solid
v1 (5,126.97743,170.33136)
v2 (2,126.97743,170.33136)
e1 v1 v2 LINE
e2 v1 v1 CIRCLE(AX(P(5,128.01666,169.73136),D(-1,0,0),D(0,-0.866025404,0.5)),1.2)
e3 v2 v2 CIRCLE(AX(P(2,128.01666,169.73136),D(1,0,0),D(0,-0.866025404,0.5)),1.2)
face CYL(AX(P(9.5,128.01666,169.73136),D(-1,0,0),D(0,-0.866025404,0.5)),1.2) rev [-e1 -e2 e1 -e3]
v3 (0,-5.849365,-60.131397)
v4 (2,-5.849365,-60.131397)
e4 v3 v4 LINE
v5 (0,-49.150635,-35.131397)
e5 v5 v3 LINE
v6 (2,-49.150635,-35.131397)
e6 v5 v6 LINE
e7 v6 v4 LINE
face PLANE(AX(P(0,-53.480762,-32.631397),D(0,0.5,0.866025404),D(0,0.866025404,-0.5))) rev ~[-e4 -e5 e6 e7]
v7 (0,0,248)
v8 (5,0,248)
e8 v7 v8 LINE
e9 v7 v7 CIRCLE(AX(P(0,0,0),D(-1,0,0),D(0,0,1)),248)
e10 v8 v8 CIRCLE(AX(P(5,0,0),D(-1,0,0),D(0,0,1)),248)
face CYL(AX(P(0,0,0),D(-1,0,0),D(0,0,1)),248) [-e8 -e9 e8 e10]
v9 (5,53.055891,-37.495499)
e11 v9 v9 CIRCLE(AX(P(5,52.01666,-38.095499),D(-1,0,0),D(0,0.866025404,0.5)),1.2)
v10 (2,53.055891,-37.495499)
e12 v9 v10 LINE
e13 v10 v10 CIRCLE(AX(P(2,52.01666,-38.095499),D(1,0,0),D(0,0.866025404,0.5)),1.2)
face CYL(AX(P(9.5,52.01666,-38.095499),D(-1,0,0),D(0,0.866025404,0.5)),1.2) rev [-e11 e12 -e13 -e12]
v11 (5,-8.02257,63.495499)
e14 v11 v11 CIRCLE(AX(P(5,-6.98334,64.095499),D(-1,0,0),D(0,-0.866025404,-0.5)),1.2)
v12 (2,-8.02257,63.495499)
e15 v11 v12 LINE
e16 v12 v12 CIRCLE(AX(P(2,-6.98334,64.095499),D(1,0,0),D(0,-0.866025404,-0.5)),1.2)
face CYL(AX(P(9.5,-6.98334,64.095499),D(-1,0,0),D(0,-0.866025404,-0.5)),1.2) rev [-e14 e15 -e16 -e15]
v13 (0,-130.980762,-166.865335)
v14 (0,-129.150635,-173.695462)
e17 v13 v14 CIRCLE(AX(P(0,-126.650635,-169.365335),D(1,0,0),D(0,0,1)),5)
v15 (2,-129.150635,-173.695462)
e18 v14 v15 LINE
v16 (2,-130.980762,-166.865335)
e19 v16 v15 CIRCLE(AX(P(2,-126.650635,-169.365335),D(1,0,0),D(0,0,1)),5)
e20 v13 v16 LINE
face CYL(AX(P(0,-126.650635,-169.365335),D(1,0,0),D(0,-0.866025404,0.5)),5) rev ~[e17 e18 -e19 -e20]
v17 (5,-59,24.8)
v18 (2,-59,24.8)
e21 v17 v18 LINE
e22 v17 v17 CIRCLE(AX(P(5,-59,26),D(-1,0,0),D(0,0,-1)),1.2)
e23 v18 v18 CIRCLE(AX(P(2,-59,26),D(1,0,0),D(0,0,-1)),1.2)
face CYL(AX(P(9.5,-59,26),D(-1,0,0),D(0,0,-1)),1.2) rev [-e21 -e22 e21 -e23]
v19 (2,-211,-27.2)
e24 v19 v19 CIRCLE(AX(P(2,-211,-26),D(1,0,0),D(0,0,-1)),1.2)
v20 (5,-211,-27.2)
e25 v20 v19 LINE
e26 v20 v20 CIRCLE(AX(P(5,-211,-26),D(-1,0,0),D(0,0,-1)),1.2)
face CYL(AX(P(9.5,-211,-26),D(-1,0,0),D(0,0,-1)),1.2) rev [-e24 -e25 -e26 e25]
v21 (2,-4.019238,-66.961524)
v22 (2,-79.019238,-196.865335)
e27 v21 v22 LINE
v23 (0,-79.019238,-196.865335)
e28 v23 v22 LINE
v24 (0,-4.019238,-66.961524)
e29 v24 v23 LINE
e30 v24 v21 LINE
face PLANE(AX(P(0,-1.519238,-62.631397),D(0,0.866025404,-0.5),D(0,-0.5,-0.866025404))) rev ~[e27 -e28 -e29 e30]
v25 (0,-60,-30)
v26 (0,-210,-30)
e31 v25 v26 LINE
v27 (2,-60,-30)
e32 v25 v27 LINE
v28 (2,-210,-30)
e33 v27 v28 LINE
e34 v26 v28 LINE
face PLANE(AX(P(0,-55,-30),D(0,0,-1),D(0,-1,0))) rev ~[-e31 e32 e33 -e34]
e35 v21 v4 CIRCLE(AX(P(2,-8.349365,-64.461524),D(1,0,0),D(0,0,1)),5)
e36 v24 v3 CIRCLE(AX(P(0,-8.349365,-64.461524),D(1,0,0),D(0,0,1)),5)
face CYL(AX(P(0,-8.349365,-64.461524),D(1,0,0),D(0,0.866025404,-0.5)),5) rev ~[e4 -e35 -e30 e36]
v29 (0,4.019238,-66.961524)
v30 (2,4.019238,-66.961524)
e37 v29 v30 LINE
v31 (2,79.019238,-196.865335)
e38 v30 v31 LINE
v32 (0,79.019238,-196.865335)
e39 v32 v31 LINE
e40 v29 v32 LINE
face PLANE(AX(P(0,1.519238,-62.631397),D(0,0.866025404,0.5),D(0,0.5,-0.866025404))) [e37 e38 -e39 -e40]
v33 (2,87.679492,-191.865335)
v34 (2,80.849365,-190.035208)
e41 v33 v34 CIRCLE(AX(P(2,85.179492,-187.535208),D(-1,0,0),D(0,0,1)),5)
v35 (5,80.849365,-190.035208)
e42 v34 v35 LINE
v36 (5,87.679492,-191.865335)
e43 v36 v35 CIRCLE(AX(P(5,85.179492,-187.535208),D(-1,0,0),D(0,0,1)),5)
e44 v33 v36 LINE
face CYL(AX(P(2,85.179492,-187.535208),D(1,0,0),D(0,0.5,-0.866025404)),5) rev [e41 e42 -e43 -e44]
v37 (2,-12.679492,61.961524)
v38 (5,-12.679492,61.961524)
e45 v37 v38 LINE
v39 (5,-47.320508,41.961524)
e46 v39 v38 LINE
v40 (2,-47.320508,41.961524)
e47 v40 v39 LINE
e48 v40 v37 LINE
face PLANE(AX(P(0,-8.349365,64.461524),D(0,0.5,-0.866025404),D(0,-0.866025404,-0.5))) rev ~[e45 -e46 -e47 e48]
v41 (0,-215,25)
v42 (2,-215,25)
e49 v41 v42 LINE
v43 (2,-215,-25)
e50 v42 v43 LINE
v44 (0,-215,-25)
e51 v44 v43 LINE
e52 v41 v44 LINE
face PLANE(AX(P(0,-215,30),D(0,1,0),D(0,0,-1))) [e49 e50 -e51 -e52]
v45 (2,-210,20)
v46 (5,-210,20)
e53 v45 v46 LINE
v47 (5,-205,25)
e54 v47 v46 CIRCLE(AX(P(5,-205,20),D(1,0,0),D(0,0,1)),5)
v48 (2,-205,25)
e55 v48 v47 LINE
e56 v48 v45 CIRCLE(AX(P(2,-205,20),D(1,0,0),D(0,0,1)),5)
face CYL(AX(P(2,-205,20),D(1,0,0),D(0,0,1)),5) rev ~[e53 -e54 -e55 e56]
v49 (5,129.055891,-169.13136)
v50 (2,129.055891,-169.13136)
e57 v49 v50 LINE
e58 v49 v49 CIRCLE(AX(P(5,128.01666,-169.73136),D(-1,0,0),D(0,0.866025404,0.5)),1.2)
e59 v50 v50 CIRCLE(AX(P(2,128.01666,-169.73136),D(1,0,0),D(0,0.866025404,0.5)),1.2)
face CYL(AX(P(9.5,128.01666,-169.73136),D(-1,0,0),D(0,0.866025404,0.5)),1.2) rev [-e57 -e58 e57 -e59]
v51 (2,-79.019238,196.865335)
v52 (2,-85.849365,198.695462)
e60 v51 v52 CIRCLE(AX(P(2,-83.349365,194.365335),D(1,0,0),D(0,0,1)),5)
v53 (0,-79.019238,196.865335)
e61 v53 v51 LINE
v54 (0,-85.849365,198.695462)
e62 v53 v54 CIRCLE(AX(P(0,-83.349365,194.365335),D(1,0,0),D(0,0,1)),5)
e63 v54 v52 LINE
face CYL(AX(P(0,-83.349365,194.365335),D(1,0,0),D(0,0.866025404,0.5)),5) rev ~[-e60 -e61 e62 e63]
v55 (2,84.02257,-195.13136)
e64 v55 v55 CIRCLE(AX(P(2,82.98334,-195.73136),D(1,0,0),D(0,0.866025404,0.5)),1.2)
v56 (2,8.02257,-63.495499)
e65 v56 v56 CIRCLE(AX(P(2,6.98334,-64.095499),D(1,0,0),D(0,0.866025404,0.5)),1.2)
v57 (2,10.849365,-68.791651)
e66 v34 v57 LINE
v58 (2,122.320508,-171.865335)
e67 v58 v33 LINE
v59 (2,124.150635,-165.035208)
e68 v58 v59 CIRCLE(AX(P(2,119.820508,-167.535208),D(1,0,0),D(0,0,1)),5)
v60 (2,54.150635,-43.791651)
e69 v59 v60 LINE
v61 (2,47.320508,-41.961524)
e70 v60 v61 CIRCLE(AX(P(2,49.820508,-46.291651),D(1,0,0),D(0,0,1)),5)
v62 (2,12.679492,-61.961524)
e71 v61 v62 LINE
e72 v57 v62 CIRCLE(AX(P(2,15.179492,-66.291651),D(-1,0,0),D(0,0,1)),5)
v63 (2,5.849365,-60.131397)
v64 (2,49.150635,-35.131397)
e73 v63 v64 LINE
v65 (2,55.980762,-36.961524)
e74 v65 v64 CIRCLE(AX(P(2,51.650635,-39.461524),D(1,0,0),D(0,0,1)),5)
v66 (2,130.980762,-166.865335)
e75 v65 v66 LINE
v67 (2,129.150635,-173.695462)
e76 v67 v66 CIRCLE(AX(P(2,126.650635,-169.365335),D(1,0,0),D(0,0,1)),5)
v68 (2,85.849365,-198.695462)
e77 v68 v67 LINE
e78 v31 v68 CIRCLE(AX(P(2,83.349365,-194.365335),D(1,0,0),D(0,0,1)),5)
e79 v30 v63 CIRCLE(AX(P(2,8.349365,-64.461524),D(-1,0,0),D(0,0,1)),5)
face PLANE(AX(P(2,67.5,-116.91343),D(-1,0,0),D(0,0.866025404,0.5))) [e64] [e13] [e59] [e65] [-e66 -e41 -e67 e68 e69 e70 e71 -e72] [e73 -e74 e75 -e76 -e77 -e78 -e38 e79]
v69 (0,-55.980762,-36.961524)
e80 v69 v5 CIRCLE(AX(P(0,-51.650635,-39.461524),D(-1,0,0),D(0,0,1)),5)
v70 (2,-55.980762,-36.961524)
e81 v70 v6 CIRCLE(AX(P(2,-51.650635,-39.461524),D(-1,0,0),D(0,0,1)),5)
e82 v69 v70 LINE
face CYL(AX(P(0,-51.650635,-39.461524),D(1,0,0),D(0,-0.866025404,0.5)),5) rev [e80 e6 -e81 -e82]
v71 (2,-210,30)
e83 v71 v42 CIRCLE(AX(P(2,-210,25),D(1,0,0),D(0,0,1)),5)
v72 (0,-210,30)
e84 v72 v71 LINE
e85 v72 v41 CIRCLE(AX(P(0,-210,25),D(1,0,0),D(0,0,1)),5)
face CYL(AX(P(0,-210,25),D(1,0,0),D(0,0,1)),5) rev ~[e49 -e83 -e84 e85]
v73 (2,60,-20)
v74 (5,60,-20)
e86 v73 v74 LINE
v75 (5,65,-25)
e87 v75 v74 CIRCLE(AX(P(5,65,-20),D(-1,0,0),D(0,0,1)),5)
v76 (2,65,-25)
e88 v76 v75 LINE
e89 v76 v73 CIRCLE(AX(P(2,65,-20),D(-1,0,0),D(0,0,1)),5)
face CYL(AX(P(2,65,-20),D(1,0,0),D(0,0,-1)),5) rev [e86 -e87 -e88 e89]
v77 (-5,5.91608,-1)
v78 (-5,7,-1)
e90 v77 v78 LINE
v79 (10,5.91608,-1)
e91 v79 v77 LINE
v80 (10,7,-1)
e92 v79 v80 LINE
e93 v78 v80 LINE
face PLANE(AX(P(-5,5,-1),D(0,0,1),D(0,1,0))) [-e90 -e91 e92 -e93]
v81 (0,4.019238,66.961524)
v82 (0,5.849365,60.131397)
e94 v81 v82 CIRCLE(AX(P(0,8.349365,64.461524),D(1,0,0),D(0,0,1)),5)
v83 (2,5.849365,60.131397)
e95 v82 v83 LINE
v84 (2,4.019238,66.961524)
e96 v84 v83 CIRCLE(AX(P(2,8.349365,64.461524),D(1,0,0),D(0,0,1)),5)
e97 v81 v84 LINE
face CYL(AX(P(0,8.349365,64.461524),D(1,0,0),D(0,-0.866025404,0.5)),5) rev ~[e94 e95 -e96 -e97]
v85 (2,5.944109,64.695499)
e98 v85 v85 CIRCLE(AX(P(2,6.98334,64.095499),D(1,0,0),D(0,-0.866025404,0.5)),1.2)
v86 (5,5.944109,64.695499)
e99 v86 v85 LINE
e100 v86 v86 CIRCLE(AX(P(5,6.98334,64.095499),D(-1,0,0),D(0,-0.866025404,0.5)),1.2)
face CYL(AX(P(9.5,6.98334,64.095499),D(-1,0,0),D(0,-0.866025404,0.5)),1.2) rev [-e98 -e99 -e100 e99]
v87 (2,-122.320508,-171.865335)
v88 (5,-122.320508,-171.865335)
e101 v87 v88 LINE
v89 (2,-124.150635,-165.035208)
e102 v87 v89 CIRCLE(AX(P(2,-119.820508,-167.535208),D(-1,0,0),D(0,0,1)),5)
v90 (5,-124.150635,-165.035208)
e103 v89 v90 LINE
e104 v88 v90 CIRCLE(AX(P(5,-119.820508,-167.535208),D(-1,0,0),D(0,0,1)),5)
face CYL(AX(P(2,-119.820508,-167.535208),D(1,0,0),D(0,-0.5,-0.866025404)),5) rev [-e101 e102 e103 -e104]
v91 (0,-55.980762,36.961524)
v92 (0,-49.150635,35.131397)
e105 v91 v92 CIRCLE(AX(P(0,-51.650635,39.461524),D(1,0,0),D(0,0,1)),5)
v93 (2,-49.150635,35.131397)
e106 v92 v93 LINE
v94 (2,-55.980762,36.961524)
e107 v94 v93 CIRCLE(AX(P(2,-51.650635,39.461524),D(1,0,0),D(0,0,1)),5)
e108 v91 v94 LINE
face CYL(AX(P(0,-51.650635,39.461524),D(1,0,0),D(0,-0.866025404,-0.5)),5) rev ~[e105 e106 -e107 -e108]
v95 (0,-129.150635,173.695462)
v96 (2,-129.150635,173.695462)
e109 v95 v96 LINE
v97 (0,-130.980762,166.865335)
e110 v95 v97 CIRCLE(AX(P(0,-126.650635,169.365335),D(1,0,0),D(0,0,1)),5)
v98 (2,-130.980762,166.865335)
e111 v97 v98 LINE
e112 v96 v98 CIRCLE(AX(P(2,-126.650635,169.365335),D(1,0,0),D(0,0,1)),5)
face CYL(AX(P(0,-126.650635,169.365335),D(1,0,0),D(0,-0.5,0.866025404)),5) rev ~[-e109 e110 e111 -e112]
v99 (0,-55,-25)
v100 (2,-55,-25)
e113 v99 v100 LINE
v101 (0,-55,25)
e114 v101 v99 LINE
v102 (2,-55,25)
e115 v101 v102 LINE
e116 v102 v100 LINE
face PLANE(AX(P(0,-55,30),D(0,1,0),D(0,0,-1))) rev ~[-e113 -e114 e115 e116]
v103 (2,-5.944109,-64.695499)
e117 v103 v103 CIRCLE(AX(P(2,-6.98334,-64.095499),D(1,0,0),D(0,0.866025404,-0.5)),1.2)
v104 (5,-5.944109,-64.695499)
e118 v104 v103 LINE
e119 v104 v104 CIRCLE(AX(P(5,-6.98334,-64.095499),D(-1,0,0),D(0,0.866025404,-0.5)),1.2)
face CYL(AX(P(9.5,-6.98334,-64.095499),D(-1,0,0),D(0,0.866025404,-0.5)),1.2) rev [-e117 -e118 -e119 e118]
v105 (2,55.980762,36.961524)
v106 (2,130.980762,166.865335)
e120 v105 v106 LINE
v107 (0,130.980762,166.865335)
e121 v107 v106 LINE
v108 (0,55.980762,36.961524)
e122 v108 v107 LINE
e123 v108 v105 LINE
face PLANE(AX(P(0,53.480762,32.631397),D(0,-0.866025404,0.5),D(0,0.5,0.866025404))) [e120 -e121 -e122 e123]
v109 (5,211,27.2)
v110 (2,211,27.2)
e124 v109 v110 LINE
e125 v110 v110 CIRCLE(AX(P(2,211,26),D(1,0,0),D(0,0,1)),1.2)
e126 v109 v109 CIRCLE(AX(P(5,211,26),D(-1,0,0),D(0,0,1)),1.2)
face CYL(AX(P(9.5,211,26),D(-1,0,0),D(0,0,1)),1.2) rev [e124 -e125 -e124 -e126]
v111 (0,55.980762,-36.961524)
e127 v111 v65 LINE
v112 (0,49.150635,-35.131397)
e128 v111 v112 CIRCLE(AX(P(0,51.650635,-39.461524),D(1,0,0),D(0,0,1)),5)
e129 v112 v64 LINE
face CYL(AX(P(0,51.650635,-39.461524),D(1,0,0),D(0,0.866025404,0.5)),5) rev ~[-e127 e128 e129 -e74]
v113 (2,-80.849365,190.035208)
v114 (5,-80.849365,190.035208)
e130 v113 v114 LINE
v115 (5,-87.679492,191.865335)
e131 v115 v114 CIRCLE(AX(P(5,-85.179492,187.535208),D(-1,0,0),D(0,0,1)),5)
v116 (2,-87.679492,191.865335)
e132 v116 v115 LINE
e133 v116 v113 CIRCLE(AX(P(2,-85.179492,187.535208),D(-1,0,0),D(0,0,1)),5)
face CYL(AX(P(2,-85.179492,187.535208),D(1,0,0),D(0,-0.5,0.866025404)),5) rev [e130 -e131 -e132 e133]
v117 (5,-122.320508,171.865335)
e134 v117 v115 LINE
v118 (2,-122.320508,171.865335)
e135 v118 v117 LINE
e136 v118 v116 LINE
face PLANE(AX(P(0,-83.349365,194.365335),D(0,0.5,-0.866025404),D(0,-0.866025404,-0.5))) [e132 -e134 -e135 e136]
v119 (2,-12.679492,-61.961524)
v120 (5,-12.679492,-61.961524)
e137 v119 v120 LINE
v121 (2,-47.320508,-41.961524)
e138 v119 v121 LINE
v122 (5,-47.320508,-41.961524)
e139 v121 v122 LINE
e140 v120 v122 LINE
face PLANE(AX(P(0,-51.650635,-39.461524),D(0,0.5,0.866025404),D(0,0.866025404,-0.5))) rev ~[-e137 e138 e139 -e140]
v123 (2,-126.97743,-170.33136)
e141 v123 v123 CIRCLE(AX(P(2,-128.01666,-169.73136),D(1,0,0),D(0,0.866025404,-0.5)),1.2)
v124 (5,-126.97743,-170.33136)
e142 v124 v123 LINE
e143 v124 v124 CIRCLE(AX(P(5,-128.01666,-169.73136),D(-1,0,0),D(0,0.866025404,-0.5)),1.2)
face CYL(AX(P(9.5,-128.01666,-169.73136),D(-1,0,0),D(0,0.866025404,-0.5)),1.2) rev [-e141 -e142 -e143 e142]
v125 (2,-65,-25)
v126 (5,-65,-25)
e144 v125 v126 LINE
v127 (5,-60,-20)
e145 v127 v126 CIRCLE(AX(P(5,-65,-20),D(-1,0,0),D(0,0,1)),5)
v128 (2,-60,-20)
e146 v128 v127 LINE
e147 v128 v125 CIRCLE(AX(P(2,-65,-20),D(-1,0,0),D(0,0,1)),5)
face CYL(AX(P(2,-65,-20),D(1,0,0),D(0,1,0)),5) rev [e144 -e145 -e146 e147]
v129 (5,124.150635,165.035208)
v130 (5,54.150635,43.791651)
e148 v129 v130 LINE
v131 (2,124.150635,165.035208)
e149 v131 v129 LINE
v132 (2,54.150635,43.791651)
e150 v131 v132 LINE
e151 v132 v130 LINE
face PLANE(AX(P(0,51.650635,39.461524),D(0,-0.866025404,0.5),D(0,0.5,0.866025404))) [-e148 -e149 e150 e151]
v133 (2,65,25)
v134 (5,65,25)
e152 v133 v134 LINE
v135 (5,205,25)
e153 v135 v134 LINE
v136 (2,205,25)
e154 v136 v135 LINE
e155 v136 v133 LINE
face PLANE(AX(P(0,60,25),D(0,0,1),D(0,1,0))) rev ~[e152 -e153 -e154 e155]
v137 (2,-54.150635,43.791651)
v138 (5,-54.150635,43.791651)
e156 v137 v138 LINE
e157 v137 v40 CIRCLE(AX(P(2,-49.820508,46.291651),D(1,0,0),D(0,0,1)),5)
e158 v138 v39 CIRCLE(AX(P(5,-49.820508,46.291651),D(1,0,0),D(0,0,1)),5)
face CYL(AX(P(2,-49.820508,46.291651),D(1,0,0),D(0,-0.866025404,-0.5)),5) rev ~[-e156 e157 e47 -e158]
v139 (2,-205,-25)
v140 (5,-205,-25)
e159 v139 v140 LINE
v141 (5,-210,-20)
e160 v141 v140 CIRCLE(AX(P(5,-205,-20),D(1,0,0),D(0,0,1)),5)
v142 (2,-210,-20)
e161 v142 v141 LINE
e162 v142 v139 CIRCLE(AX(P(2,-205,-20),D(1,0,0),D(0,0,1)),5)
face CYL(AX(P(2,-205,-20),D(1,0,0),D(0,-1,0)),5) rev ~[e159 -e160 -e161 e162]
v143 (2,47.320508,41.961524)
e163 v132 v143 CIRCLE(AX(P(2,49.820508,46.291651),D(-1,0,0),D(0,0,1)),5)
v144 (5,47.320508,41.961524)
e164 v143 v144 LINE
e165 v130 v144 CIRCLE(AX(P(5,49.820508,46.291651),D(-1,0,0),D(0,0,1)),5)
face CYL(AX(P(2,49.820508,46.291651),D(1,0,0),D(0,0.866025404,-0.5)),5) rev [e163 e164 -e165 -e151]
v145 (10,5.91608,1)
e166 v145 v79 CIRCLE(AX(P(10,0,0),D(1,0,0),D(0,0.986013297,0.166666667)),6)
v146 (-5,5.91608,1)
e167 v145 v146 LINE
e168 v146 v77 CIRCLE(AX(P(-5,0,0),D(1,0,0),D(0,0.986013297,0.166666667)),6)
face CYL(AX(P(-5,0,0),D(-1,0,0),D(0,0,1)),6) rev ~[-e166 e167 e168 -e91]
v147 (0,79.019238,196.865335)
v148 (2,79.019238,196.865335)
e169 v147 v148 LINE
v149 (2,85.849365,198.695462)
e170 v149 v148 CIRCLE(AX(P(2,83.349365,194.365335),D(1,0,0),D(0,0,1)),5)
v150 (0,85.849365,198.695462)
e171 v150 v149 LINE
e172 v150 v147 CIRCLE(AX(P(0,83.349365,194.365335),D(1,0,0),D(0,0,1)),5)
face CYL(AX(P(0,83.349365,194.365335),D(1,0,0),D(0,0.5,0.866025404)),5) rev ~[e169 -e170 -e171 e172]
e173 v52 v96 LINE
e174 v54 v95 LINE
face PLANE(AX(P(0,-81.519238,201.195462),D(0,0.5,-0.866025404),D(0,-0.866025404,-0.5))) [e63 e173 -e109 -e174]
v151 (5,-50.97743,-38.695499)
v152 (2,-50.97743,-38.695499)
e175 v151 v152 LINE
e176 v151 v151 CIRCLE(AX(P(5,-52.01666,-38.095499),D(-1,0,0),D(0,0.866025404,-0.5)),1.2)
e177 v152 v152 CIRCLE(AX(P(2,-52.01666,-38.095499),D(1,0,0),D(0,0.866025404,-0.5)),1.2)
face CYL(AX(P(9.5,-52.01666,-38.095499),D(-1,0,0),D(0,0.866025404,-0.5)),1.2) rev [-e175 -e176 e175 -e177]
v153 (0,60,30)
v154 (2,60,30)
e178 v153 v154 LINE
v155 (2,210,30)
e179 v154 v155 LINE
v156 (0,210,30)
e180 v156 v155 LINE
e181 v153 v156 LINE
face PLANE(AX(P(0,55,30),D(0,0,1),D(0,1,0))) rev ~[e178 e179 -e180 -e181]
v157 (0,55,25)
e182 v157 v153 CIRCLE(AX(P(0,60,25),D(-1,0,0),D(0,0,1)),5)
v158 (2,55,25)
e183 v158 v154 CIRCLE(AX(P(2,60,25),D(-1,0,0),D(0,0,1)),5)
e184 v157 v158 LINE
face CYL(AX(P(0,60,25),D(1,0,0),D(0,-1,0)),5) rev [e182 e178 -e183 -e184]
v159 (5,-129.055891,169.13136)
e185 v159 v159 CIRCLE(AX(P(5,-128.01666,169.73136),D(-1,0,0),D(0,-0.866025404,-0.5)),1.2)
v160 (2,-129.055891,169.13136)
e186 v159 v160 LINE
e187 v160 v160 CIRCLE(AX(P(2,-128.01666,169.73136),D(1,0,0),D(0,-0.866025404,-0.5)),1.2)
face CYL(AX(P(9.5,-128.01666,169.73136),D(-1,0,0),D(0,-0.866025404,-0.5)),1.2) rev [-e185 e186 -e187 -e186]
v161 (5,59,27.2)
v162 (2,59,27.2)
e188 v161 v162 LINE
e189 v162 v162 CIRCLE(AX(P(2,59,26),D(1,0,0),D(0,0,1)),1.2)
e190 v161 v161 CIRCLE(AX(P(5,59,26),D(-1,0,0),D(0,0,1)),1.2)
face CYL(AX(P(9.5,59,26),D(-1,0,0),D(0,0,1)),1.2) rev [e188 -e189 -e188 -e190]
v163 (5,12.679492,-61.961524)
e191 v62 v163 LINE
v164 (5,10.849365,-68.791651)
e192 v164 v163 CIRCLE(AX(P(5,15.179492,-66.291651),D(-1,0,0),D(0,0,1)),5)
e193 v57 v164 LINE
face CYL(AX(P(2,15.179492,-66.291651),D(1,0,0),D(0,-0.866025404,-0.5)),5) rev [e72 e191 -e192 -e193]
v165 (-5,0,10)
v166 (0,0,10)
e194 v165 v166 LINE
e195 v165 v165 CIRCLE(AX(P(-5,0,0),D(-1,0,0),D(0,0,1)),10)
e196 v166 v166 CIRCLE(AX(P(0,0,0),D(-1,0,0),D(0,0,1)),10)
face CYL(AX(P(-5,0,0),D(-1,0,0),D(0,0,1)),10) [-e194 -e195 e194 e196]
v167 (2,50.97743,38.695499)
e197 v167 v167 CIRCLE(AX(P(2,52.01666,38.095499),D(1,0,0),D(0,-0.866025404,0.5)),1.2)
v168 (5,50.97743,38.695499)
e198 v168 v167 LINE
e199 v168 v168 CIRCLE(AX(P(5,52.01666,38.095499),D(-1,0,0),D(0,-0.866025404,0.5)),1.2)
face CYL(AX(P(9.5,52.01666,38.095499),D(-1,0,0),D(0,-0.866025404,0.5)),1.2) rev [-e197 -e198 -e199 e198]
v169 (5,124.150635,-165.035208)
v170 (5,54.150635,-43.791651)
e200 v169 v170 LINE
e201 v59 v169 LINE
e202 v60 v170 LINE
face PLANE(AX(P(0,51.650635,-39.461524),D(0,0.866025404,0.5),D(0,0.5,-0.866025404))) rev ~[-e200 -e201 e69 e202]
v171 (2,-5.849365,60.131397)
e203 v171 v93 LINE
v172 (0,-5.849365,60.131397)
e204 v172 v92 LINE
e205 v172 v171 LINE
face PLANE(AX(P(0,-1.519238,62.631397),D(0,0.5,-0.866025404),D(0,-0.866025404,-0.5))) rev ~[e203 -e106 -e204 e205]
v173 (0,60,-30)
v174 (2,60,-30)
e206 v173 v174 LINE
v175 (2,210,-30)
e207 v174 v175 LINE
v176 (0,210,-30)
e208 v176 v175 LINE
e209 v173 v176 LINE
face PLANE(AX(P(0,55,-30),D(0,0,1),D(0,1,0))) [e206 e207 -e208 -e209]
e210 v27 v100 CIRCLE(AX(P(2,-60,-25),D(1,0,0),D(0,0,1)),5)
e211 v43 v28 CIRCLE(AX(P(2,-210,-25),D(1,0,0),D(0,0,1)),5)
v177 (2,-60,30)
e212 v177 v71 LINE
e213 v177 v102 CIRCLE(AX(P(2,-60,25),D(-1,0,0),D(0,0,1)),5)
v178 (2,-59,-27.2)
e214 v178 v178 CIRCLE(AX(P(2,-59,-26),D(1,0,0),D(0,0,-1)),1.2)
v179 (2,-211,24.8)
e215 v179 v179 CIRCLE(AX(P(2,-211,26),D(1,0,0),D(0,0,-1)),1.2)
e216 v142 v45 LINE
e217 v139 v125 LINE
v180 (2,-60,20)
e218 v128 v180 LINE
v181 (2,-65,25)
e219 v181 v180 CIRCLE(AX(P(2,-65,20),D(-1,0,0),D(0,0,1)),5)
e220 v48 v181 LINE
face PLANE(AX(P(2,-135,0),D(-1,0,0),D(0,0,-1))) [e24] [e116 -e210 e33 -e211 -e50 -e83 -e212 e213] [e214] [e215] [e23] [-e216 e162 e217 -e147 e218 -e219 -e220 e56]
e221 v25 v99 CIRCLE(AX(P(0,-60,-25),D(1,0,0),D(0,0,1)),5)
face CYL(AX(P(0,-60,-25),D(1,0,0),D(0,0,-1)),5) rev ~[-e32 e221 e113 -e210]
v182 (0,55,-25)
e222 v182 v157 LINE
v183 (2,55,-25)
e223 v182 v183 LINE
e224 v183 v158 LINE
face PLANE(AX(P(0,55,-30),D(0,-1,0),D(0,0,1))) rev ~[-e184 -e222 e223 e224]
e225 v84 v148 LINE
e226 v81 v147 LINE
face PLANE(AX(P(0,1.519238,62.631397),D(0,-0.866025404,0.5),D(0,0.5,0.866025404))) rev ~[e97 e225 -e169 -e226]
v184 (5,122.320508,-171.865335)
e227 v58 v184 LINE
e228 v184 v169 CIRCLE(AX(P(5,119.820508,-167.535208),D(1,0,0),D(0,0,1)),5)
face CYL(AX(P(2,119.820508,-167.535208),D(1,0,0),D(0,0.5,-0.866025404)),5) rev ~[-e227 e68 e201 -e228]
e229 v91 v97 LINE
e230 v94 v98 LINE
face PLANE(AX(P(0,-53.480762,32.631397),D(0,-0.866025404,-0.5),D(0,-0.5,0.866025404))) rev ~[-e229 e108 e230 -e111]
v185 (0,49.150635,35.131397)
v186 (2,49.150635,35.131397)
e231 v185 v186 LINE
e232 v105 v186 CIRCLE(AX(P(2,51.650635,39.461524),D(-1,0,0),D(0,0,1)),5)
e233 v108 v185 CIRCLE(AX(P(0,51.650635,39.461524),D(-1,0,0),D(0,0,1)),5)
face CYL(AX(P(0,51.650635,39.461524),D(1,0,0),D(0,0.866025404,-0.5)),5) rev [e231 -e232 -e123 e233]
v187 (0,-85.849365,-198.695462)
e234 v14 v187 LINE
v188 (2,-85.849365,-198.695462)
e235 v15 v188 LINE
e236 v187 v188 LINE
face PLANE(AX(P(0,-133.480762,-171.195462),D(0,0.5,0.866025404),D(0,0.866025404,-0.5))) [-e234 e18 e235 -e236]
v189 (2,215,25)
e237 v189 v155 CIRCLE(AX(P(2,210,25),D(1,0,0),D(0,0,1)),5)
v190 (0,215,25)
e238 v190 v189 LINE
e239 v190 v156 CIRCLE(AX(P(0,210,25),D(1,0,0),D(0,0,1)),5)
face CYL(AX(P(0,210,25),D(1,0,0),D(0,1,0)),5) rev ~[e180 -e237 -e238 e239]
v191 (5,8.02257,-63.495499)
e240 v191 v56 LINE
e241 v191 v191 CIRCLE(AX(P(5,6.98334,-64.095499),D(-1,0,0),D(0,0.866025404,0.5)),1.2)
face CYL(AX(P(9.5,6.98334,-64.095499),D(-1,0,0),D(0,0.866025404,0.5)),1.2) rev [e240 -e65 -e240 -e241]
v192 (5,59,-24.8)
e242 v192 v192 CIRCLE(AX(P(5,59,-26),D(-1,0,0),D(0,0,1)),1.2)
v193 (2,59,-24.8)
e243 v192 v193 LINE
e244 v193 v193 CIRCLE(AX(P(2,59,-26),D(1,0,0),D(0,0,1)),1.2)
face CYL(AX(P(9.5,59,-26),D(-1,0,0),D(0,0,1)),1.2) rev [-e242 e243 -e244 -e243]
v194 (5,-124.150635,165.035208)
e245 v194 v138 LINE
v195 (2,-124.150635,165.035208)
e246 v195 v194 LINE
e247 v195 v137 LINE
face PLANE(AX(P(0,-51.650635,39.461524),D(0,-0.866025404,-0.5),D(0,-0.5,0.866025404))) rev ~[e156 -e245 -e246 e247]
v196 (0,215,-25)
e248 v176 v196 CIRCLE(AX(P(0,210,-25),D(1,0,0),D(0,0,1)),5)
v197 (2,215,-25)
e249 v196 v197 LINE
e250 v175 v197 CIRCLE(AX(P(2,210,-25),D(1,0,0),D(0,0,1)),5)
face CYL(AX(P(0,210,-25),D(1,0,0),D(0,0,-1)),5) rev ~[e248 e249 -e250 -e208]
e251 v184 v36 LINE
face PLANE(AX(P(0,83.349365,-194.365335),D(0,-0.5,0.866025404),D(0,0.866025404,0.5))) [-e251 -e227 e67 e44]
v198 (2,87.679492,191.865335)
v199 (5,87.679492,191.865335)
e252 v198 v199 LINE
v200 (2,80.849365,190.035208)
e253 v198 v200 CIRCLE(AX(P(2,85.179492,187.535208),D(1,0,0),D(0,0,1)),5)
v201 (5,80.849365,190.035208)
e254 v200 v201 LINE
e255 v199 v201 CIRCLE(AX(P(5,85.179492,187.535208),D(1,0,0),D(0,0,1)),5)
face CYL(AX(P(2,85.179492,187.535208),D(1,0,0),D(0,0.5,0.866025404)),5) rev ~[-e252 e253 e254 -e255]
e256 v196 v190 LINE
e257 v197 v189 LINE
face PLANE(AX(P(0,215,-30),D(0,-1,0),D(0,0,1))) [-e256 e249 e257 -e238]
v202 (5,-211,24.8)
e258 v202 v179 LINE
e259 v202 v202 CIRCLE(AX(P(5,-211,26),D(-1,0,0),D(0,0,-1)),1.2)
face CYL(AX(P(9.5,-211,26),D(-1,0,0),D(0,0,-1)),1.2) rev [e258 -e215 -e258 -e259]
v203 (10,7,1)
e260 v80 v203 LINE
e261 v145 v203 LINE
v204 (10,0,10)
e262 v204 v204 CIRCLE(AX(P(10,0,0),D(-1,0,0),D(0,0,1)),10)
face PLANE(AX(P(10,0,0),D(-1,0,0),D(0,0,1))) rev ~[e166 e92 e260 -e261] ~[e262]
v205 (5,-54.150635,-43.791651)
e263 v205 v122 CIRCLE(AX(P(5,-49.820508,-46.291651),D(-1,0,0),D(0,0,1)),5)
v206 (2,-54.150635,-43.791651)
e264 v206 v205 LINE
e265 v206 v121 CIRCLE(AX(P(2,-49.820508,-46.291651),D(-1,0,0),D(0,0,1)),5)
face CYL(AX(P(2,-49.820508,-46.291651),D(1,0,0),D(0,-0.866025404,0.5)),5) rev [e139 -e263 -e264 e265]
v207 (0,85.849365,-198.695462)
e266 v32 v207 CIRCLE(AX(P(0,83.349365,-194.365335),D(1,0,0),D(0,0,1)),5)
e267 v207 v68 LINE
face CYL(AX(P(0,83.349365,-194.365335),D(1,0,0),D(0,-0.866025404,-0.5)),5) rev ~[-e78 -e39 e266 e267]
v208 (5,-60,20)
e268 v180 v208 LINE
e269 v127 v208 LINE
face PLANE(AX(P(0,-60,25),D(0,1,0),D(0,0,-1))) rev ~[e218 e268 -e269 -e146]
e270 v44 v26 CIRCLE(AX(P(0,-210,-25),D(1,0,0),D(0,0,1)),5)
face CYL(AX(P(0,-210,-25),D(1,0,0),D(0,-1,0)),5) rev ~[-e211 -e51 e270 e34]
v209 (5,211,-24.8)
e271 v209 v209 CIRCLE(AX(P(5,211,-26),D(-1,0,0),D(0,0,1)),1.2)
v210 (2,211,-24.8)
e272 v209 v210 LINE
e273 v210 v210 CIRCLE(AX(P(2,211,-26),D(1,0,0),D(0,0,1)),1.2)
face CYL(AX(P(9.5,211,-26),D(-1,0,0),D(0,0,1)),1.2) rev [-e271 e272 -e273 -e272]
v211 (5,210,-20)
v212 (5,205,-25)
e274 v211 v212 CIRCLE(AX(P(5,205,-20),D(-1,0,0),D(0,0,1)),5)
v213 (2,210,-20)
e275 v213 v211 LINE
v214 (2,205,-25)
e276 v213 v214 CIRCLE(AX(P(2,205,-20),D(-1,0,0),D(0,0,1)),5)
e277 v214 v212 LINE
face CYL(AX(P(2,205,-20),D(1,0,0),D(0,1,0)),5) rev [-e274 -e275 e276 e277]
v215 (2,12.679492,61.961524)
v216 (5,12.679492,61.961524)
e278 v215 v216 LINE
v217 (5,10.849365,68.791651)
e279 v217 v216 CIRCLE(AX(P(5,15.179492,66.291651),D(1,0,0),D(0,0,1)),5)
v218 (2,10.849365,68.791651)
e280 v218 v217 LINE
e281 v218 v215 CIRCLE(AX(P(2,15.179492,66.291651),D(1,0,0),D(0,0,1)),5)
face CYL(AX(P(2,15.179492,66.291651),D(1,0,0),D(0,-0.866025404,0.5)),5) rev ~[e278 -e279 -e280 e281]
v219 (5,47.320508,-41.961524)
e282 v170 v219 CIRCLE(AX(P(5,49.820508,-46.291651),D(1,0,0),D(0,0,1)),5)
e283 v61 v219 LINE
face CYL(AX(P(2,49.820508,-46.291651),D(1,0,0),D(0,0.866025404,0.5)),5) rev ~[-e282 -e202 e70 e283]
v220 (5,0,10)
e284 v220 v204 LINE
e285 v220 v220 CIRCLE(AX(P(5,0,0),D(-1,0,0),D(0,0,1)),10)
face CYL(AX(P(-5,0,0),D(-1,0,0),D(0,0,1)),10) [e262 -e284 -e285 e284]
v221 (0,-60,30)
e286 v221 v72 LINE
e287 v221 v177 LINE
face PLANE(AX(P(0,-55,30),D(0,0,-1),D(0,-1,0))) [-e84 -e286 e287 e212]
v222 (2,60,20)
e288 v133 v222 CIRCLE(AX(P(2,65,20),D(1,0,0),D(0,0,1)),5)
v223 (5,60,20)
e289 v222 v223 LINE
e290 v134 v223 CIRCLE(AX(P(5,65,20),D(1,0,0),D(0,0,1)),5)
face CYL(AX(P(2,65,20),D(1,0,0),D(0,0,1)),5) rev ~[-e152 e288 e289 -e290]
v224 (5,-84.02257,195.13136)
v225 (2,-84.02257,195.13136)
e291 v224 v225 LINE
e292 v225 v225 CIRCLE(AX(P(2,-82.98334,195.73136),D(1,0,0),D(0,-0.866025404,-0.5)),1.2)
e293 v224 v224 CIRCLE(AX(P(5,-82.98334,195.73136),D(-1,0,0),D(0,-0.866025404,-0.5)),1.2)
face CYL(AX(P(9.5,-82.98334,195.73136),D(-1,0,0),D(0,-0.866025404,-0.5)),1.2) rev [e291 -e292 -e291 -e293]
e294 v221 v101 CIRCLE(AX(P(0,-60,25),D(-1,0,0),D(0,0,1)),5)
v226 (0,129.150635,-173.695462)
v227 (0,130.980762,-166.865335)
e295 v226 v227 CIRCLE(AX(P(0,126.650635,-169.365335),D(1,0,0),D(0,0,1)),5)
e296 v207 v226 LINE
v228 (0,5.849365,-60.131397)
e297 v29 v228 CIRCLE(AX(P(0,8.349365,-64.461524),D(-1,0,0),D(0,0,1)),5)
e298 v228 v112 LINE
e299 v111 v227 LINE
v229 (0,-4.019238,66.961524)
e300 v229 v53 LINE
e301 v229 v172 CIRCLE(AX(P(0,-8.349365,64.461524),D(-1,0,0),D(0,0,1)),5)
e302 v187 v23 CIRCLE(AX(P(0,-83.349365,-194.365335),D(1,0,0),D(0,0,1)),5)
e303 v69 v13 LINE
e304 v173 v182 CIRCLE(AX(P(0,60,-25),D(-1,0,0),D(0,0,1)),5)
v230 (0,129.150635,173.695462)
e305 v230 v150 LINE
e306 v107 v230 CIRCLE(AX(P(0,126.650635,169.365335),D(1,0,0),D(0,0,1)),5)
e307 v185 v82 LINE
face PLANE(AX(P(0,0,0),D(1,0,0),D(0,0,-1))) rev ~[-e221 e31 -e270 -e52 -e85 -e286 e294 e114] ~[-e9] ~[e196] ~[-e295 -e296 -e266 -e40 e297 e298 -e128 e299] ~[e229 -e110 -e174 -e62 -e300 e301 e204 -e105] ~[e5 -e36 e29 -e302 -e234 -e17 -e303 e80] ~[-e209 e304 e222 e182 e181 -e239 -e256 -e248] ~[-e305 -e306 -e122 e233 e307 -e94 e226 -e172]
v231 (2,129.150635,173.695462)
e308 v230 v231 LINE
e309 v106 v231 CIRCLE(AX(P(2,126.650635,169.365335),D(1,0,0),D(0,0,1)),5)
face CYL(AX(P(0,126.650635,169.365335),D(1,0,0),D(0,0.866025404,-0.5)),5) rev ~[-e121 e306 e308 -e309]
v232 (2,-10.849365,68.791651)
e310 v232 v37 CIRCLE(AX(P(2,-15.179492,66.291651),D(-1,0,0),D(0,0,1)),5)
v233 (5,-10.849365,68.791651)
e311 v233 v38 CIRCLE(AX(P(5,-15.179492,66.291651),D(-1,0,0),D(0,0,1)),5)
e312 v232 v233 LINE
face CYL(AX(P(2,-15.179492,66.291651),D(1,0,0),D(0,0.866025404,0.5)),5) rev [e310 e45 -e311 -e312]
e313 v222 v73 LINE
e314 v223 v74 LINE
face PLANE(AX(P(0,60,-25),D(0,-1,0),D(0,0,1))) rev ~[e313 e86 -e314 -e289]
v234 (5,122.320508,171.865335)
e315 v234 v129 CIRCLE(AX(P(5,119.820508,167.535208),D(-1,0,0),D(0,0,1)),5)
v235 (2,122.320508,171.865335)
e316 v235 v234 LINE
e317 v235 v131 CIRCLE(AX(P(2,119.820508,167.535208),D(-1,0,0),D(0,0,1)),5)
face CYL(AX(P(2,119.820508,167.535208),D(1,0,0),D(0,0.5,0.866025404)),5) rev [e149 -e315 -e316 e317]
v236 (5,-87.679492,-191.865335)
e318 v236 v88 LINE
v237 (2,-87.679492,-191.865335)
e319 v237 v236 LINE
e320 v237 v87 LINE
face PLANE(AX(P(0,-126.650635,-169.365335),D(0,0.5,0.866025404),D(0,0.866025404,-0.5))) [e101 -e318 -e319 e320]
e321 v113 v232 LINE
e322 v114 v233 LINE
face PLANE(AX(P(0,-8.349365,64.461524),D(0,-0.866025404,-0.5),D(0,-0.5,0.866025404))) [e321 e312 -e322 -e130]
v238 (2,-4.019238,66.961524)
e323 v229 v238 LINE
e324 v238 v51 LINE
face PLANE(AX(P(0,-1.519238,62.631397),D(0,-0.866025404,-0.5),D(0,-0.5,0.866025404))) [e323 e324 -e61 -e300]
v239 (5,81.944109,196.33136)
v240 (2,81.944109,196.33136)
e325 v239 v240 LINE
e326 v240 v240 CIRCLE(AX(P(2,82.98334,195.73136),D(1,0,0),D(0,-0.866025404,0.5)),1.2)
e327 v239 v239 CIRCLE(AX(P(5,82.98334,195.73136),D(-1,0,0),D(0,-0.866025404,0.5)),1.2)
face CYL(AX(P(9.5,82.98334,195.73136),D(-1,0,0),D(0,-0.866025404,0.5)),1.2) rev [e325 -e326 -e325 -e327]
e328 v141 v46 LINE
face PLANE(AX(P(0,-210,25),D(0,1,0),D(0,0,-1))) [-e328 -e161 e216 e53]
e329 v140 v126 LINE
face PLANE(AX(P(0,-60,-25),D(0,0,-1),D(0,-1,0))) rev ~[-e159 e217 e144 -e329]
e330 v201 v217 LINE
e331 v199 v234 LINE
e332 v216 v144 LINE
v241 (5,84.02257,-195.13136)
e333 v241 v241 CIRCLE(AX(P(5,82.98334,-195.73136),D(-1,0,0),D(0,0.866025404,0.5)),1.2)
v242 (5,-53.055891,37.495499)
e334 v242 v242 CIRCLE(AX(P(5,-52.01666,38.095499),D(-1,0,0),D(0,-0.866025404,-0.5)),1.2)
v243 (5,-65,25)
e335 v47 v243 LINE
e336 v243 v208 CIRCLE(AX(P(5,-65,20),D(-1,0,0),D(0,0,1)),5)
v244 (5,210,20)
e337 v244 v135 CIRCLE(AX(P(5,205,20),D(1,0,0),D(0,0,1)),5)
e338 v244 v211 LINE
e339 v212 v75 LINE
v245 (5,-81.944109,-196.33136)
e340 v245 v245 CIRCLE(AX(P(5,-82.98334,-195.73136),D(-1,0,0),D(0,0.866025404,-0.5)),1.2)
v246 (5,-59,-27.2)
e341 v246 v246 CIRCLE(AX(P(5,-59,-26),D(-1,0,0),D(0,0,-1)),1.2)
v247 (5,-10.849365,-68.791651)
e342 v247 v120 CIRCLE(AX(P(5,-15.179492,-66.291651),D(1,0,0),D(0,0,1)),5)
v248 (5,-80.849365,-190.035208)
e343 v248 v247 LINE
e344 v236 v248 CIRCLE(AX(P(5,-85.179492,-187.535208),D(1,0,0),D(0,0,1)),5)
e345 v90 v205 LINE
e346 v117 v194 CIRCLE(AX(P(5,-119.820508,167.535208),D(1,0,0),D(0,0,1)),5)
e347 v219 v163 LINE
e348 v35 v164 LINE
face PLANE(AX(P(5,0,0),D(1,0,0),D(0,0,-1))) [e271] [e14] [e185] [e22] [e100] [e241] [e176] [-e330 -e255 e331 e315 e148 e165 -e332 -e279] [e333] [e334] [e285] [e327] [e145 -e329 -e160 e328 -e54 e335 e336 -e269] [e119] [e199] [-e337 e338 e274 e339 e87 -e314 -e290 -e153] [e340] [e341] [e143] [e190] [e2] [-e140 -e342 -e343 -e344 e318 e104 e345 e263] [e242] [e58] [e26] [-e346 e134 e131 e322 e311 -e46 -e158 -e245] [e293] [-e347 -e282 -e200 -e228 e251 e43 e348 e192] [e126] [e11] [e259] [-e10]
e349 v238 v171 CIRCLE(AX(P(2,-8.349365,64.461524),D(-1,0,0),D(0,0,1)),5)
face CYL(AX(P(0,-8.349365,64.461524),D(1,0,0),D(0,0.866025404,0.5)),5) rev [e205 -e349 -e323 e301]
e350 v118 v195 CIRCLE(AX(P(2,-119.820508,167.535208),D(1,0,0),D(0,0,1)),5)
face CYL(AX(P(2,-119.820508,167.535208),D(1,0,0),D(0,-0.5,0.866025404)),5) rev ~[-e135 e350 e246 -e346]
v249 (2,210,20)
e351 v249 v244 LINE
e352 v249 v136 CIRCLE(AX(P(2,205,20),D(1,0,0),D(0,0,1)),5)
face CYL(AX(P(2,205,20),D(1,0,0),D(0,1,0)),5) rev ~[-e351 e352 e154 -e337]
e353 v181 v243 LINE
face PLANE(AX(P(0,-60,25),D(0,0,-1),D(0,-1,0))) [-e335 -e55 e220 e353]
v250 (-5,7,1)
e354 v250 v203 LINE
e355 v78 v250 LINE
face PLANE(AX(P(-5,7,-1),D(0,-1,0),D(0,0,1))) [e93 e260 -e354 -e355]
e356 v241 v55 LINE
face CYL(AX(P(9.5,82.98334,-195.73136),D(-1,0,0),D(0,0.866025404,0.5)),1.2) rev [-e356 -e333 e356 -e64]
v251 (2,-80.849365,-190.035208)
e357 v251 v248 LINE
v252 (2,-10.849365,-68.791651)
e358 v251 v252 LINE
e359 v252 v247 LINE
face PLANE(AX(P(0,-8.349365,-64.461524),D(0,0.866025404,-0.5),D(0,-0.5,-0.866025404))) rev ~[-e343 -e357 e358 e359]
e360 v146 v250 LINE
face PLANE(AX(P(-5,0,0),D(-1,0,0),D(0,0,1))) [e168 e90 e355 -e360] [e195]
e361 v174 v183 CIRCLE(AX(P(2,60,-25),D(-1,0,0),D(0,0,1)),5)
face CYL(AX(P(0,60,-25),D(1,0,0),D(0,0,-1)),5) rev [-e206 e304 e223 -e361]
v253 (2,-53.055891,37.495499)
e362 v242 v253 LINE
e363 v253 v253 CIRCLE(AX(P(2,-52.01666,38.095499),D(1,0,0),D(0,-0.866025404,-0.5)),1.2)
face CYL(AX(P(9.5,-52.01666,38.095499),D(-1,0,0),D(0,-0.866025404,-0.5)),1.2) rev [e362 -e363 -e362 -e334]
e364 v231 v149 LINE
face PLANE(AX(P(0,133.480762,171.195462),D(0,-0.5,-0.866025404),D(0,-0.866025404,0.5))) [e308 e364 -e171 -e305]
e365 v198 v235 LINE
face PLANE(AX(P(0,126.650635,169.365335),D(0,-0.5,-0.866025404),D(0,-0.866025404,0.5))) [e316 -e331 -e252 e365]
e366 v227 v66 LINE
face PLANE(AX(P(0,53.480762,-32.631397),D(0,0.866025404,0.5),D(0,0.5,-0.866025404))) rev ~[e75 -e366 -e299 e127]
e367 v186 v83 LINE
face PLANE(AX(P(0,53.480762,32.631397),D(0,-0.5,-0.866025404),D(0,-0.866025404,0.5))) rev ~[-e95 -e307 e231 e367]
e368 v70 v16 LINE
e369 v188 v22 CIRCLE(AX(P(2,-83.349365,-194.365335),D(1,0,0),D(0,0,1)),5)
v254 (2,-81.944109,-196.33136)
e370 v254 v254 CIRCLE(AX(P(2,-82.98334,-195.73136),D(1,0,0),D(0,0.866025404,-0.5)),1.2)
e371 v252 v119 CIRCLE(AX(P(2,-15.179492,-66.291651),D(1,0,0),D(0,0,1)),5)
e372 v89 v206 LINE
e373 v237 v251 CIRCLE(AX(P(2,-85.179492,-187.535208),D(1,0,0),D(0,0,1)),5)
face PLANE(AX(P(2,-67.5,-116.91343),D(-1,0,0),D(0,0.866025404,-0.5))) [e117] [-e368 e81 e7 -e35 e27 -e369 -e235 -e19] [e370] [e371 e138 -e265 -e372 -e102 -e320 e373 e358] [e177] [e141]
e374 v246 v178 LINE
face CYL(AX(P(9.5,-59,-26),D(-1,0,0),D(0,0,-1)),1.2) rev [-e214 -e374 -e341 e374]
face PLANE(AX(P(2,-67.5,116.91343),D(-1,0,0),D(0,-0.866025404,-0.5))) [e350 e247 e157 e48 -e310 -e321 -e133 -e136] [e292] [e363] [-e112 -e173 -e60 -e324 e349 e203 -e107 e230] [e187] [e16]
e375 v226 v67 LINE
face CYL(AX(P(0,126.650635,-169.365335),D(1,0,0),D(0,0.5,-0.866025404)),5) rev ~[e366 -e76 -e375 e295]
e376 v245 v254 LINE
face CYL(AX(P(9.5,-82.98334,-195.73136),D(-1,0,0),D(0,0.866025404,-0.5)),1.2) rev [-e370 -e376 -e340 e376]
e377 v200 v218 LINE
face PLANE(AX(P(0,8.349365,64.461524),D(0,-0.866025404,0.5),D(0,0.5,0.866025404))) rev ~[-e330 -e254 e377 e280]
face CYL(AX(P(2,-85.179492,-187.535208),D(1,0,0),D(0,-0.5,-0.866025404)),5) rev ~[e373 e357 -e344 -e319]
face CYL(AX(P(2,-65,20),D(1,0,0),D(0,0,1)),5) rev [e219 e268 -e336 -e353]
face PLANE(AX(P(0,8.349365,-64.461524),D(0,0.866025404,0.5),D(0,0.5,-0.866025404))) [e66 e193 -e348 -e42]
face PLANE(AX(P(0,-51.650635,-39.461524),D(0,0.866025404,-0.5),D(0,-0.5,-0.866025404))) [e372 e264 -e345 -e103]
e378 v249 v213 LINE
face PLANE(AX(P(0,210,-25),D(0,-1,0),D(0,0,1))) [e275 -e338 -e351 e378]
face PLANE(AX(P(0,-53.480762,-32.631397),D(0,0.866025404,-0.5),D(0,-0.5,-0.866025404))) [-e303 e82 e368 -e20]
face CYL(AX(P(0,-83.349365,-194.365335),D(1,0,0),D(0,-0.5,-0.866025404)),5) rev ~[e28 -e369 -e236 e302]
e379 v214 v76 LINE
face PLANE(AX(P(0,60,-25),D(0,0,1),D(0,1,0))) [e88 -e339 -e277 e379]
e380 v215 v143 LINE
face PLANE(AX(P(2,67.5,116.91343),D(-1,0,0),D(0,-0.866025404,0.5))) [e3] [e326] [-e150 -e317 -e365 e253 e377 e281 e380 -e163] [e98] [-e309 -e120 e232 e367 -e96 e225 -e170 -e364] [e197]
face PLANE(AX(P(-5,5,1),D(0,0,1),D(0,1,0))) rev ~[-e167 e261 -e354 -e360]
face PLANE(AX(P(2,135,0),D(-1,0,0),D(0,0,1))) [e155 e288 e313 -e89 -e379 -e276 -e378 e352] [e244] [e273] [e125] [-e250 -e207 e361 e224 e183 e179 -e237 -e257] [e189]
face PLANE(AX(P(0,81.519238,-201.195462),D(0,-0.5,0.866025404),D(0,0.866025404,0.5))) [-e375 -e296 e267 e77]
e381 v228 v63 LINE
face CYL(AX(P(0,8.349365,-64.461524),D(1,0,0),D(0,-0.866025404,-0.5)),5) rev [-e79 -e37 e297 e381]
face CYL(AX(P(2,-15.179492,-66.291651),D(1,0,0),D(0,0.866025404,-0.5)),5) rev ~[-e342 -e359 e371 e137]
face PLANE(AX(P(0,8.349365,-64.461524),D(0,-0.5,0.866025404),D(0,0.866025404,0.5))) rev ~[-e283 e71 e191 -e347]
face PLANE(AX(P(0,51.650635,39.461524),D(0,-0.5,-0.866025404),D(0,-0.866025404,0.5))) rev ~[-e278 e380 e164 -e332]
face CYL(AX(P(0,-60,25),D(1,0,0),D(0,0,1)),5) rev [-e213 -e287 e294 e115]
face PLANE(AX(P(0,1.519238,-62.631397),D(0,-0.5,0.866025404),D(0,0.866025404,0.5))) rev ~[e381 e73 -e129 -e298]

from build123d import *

# Parameters (mm, degrees)
SKETCH1_R                     = 250
BOSS_EXTRUDE1_DEPTH           = 5
SKETCH5_W                     = 50
SKETCH5_H                     = 150
CUT_EXTRUDE1_DEPTH            = 354.588744165
CIRPATTERN1_COUNT             = 6
SKETCH6_W                     = 60
SKETCH6_H                     = 160
CUT_EXTRUDE2_DEPTH            = 2
SKETCH7_R                     = 1
CUT_EXTRUDE3_DEPTH            = 10
M2_CLEARANCE_HOLE1_AT_2_COUNT = 2
M2_CLEARANCE_HOLE1_AT_2_PITCH = 152
M2_CLEARANCE_HOLE1_AT_3_COUNT = 2
M2_CLEARANCE_HOLE1_AT_3_PITCH = 160.648685024
M2_CLEARANCE_HOLE1_AT_4_COUNT = 2
M2_CLEARANCE_HOLE1_AT_4_PITCH = 52
CIRPATTERN2_COUNT             = 6
FILLET1_R                     = 5
FILLET2_R                     = 5
SKETCH11_R                    = 6
CUT_EXTRUDE4_DEPTH            = 354.588744165
BOSS_EXTRUDE2_START           = 5
SKETCH12_R                    = 10
SKETCH12_R_2                  = 6
BOSS_EXTRUDE2_DEPTH           = 15
SKETCH13_W                    = 2
SKETCH13_H                    = 2
CUT_EXTRUDE5_DEPTH            = 354.871445584
SKETCH14_R                    = 250
SKETCH14_R_2                  = 248
CUT_EXTRUDE6_DEPTH            = 354.694783677


with BuildPart() as part:
    # Sketch1 → Boss-Extrude1 (new body)
    with BuildSketch(Plane(origin=(0, 0, 0), x_dir=(0, 0, -1), z_dir=(1, 0, 0))):
        Circle(SKETCH1_R)
    extrude(amount=BOSS_EXTRUDE1_DEPTH)

    # Sketch5 → Cut-Extrude1 (cut, through all)
    with BuildSketch(Plane.ZY):
        with Locations((0, 135)):
            Rectangle(SKETCH5_W, SKETCH5_H)
    cut_extrude1 = extrude(amount=-CUT_EXTRUDE1_DEPTH, mode=Mode.SUBTRACT)

    # CirPattern1: Cut-Extrude1 ×6 about axis
    cirpattern1_axis = Axis((0, 0, 0), (1, 0, 0))
    for i in range(1, CIRPATTERN1_COUNT):
        add(cut_extrude1.rotate(cirpattern1_axis, i * 360 / CIRPATTERN1_COUNT), mode=Mode.SUBTRACT)

    # Sketch6 → Cut-Extrude2 (cut)
    with BuildSketch(Plane.ZY):
        with Locations((0, 135)):
            Rectangle(SKETCH6_W, SKETCH6_H)
    cut_extrude2 = extrude(amount=-CUT_EXTRUDE2_DEPTH, mode=Mode.SUBTRACT)

    # Sketch7 → Cut-Extrude3 (cut)
    with BuildSketch(Plane.ZY.offset(-2)):
        with Locations((-26, 211)):
            Circle(SKETCH7_R)
        with Locations((26, 211)):
            Circle(SKETCH7_R)
        with Locations((-26, 59)):
            Circle(SKETCH7_R)
        with Locations((26, 59)):
            Circle(SKETCH7_R)
    cut_extrude3 = extrude(amount=-CUT_EXTRUDE3_DEPTH, mode=Mode.SUBTRACT)

    # Sketch9 → M2 Clearance Hole1 (revolve, cut)
    with BuildSketch(Plane(origin=(2, 59, -26), x_dir=(0, 0, 1), z_dir=(0, 1, 0))):
        Polygon((0, 0), (0, 8.221032743), (1.2, 7.5), (1.2, 0), align=None)
    m2_clearance_hole1 = revolve(axis=Axis((-4.35, 59, -26), (1, 0, 0)), mode=Mode.SUBTRACT)

    # M2 Clearance Hole1 at 2: M2 Clearance Hole1 ×2
    with Locations(*[(0, i * M2_CLEARANCE_HOLE1_AT_2_PITCH, 0) for i in range(1, M2_CLEARANCE_HOLE1_AT_2_COUNT)]):
        add(m2_clearance_hole1, mode=Mode.SUBTRACT)

    # M2 Clearance Hole1 at 3: M2 Clearance Hole1 ×2
    with Locations(*[Vector(0, 0.9461639849533562, 0.32368767906298995) * (i * M2_CLEARANCE_HOLE1_AT_3_PITCH) for i in range(1, M2_CLEARANCE_HOLE1_AT_3_COUNT)]):
        add(m2_clearance_hole1, mode=Mode.SUBTRACT)

    # M2 Clearance Hole1 at 4: M2 Clearance Hole1 ×2
    with Locations(*[(0, 0, i * M2_CLEARANCE_HOLE1_AT_4_PITCH) for i in range(1, M2_CLEARANCE_HOLE1_AT_4_COUNT)]):
        add(m2_clearance_hole1, mode=Mode.SUBTRACT)

    # CirPattern2: Cut-Extrude2, Cut-Extrude3, M2 Clearance Hole1 ×6 about axis
    cirpattern2_axis = Axis((0, 0, 0), (1, 0, 0))
    add([cut_extrude2.rotate(cirpattern2_axis, i * 360 / CIRPATTERN2_COUNT) for i in range(1, CIRPATTERN2_COUNT)], mode=Mode.SUBTRACT)
    add([cut_extrude3.rotate(cirpattern2_axis, i * 360 / CIRPATTERN2_COUNT) for i in range(1, CIRPATTERN2_COUNT)], mode=Mode.SUBTRACT)
    add([m2_clearance_hole1.rotate(cirpattern2_axis, i * 360 / CIRPATTERN2_COUNT) for i in range(1, CIRPATTERN2_COUNT)], mode=Mode.SUBTRACT)

    # CirPattern2 copy 1 sketch → CirPattern2 copy 1 (revolve, cut)
    with BuildSketch(Plane(origin=(2, 128.016660498, 169.731360199), x_dir=(0, -0.8660254037844386, 0.5000000000000001), z_dir=(0, 0.5000000000000001, 0.8660254037844386))):
        Polygon((0, 0), (0, 8.221032743), (1.2, 7.5), (1.2, 0), align=None)
    revolve(axis=Axis((-4.35, 128.016660498, 169.731360199), (1, 0, 0)), mode=Mode.SUBTRACT)

    # CirPattern2 copy 2 sketch → CirPattern2 copy 2 (revolve, cut)
    with BuildSketch(Plane(origin=(2, -82.983339502, 195.731360199), x_dir=(0, -0.8660254037844387, -0.4999999999999998), z_dir=(0, -0.4999999999999998, 0.8660254037844387))):
        Polygon((0, 0), (0, 8.221032743), (1.2, 7.5), (1.2, 0), align=None)
    revolve(axis=Axis((-4.35, -82.983339502, 195.731360199), (1, 0, 0)), mode=Mode.SUBTRACT)

    # CirPattern2 copy 3 sketch → CirPattern2 copy 3 (revolve, cut)
    with BuildSketch(Plane(origin=(2, -211, 26), x_dir=(0, 0, -1), z_dir=(0, -1, 0))):
        Polygon((0, 0), (0, 8.221032743), (1.2, 7.5), (1.2, 0), align=None)
    revolve(axis=Axis((-4.35, -211, 26), (1, 0, 0)), mode=Mode.SUBTRACT)

    # CirPattern2 copy 4 sketch → CirPattern2 copy 4 (revolve, cut)
    with BuildSketch(Plane(origin=(2, -128.016660498, -169.731360199), x_dir=(0, 0.8660254037844384, -0.5000000000000004), z_dir=(0, -0.5000000000000004, -0.8660254037844384))):
        Polygon((0, 0), (0, 8.221032743), (1.2, 7.5), (1.2, 0), align=None)
    revolve(axis=Axis((-4.35, -128.016660498, -169.731360199), (1, 0, 0)), mode=Mode.SUBTRACT)

    # CirPattern2 copy 5 sketch → CirPattern2 copy 5 (revolve, cut)
    with BuildSketch(Plane(origin=(2, 82.983339502, -195.731360199), x_dir=(0, 0.8660254037844386, 0.5000000000000001), z_dir=(0, 0.5000000000000001, -0.8660254037844386))):
        Polygon((0, 0), (0, 8.221032743), (1.2, 7.5), (1.2, 0), align=None)
    revolve(axis=Axis((-4.35, 82.983339502, -195.731360199), (1, 0, 0)), mode=Mode.SUBTRACT)

    # CirPattern2 copy 6 sketch → CirPattern2 copy 6 (revolve, cut)
    with BuildSketch(Plane(origin=(2, 82.983339502, 195.731360199), x_dir=(0, -0.8660254037844386, 0.5000000000000001), z_dir=(0, 0.5000000000000001, 0.8660254037844386))):
        Polygon((0, 0), (0, 8.221032743), (1.2, 7.5), (1.2, 0), align=None)
    revolve(axis=Axis((-4.35, 82.983339502, 195.731360199), (1, 0, 0)), mode=Mode.SUBTRACT)

    # CirPattern2 copy 7 sketch → CirPattern2 copy 7 (revolve, cut)
    with BuildSketch(Plane(origin=(2, -128.016660498, 169.731360199), x_dir=(0, -0.8660254037844387, -0.4999999999999998), z_dir=(0, -0.4999999999999998, 0.8660254037844387))):
        Polygon((0, 0), (0, 8.221032743), (1.2, 7.5), (1.2, 0), align=None)
    revolve(axis=Axis((-4.35, -128.016660498, 169.731360199), (1, 0, 0)), mode=Mode.SUBTRACT)

    # CirPattern2 copy 8 sketch → CirPattern2 copy 8 (revolve, cut)
    with BuildSketch(Plane(origin=(2, -211, -26), x_dir=(0, 0, -1), z_dir=(0, -1, 0))):
        Polygon((0, 0), (0, 8.221032743), (1.2, 7.5), (1.2, 0), align=None)
    revolve(axis=Axis((-4.35, -211, -26), (1, 0, 0)), mode=Mode.SUBTRACT)

    # CirPattern2 copy 9 sketch → CirPattern2 copy 9 (revolve, cut)
    with BuildSketch(Plane(origin=(2, -82.983339502, -195.731360199), x_dir=(0, 0.8660254037844384, -0.5000000000000004), z_dir=(0, -0.5000000000000004, -0.8660254037844384))):
        Polygon((0, 0), (0, 8.221032743), (1.2, 7.5), (1.2, 0), align=None)
    revolve(axis=Axis((-4.35, -82.983339502, -195.731360199), (1, 0, 0)), mode=Mode.SUBTRACT)

    # CirPattern2 copy 10 sketch → CirPattern2 copy 10 (revolve, cut)
    with BuildSketch(Plane(origin=(2, 128.016660498, -169.731360199), x_dir=(0, 0.8660254037844386, 0.5000000000000001), z_dir=(0, 0.5000000000000001, -0.8660254037844386))):
        Polygon((0, 0), (0, 8.221032743), (1.2, 7.5), (1.2, 0), align=None)
    revolve(axis=Axis((-4.35, 128.016660498, -169.731360199), (1, 0, 0)), mode=Mode.SUBTRACT)

    # CirPattern2 copy 11 sketch → CirPattern2 copy 11 (revolve, cut)
    with BuildSketch(Plane(origin=(2, 6.983339502, 64.095498823), x_dir=(0, -0.8660254037844386, 0.5000000000000001), z_dir=(0, 0.5000000000000001, 0.8660254037844386))):
        Polygon((0, 0), (0, 8.221032743), (1.2, 7.5), (1.2, 0), align=None)
    revolve(axis=Axis((-4.35, 6.983339502, 64.095498823), (1, 0, 0)), mode=Mode.SUBTRACT)

    # CirPattern2 copy 12 sketch → CirPattern2 copy 12 (revolve, cut)
    with BuildSketch(Plane(origin=(2, -52.016660498, 38.095498823), x_dir=(0, -0.8660254037844387, -0.4999999999999998), z_dir=(0, -0.4999999999999998, 0.8660254037844387))):
        Polygon((0, 0), (0, 8.221032743), (1.2, 7.5), (1.2, 0), align=None)
    revolve(axis=Axis((-4.35, -52.016660498, 38.095498823), (1, 0, 0)), mode=Mode.SUBTRACT)

    # CirPattern2 copy 13 sketch → CirPattern2 copy 13 (revolve, cut)
    with BuildSketch(Plane(origin=(2, -59, -26), x_dir=(0, 0, -1), z_dir=(0, -1, 0))):
        Polygon((0, 0), (0, 8.221032743), (1.2, 7.5), (1.2, 0), align=None)
    revolve(axis=Axis((-4.35, -59, -26), (1, 0, 0)), mode=Mode.SUBTRACT)

    # CirPattern2 copy 14 sketch → CirPattern2 copy 14 (revolve, cut)
    with BuildSketch(Plane(origin=(2, -6.983339502, -64.095498823), x_dir=(0, 0.8660254037844384, -0.5000000000000004), z_dir=(0, -0.5000000000000004, -0.8660254037844384))):
        Polygon((0, 0), (0, 8.221032743), (1.2, 7.5), (1.2, 0), align=None)
    revolve(axis=Axis((-4.35, -6.983339502, -64.095498823), (1, 0, 0)), mode=Mode.SUBTRACT)

    # CirPattern2 copy 15 sketch → CirPattern2 copy 15 (revolve, cut)
    with BuildSketch(Plane(origin=(2, 52.016660498, -38.095498823), x_dir=(0, 0.8660254037844386, 0.5000000000000001), z_dir=(0, 0.5000000000000001, -0.8660254037844386))):
        Polygon((0, 0), (0, 8.221032743), (1.2, 7.5), (1.2, 0), align=None)
    revolve(axis=Axis((-4.35, 52.016660498, -38.095498823), (1, 0, 0)), mode=Mode.SUBTRACT)

    # Fillet1
    fillet1_edges = [part.edges().sort_by_distance(p)[0] for p in [
        (1, 55, 30),
        (1, 1.519237886, -62.631397208),
        (1, 81.519237886, -201.195461814),
        (1, 133.480762114, -171.195461814),
        (1, 53.480762114, -32.631397208),
        (1, -53.480762114, -32.631397208),
        (1, -133.480762114, -171.195461814),
        (1, -81.519237886, -201.195461814),
        (1, -1.519237886, -62.631397208),
        (1, -55, 30),
        (1, -215, 30),
        (1, -215, -30),
        (1, -55, -30),
        (1, -1.519237886, 62.631397208),
        (1, -81.519237886, 201.195461814),
        (1, -133.480762114, 171.195461814),
        (1, -53.480762114, 32.631397208),
        (1, 53.480762114, 32.631397208),
        (1, 133.480762114, 171.195461814),
        (1, 81.519237886, 201.195461814),
        (1, 1.519237886, 62.631397208),
        (1, 55, -30),
        (1, 215, -30),
        (1, 215, 30),
    ]]
    fillet(fillet1_edges, radius=FILLET1_R)

    # Fillet2
    fillet2_edges = [part.edges().sort_by_distance(p)[0] for p in [
        (3.5, 60, 25),
        (3.5, 60, -25),
        (3.5, 210, -25),
        (3.5, 126.650635095, -169.365334795),
        (3.5, 51.650635095, -39.461524227),
        (3.5, 8.349364905, -64.461524227),
        (3.5, 83.349364905, -194.365334795),
        (3.5, -83.349364905, -194.365334795),
        (3.5, -8.349364905, -64.461524227),
        (3.5, -51.650635095, -39.461524227),
        (3.5, -126.650635095, -169.365334795),
        (3.5, -210, -25),
        (3.5, -60, -25),
        (3.5, -60, 25),
        (3.5, -210, 25),
        (3.5, -126.650635095, 169.365334795),
        (3.5, -51.650635095, 39.461524227),
        (3.5, -8.349364905, 64.461524227),
        (3.5, -83.349364905, 194.365334795),
        (3.5, 83.349364905, 194.365334795),
        (3.5, 8.349364905, 64.461524227),
        (3.5, 51.650635095, 39.461524227),
        (3.5, 126.650635095, 169.365334795),
        (3.5, 210, 25),
    ]]
    fillet(fillet2_edges, radius=FILLET2_R)

    # Sketch11 → Cut-Extrude4 (cut, through all)
    with BuildSketch(Plane.ZY):
        Circle(SKETCH11_R)
    extrude(amount=-CUT_EXTRUDE4_DEPTH, mode=Mode.SUBTRACT)

    # Sketch12 → Boss-Extrude2 (add)
    with BuildSketch(Plane.ZY.offset(BOSS_EXTRUDE2_START)):
        Circle(SKETCH12_R)
        Circle(SKETCH12_R_2, mode=Mode.SUBTRACT)
    extrude(amount=-BOSS_EXTRUDE2_DEPTH)

    # Sketch13 → Cut-Extrude5 (cut, through all)
    with BuildSketch(Plane.ZY.offset(5)):
        with Locations((0, 6)):
            Rectangle(SKETCH13_W, SKETCH13_H)
    extrude(amount=-CUT_EXTRUDE5_DEPTH, mode=Mode.SUBTRACT)

    # Sketch14 → Cut-Extrude6 (cut, through all)
    with BuildSketch(Plane.ZY):
        Circle(SKETCH14_R)
        Circle(SKETCH14_R_2, mode=Mode.SUBTRACT)
    extrude(amount=-CUT_EXTRUDE6_DEPTH, mode=Mode.SUBTRACT)


solid = part.part
